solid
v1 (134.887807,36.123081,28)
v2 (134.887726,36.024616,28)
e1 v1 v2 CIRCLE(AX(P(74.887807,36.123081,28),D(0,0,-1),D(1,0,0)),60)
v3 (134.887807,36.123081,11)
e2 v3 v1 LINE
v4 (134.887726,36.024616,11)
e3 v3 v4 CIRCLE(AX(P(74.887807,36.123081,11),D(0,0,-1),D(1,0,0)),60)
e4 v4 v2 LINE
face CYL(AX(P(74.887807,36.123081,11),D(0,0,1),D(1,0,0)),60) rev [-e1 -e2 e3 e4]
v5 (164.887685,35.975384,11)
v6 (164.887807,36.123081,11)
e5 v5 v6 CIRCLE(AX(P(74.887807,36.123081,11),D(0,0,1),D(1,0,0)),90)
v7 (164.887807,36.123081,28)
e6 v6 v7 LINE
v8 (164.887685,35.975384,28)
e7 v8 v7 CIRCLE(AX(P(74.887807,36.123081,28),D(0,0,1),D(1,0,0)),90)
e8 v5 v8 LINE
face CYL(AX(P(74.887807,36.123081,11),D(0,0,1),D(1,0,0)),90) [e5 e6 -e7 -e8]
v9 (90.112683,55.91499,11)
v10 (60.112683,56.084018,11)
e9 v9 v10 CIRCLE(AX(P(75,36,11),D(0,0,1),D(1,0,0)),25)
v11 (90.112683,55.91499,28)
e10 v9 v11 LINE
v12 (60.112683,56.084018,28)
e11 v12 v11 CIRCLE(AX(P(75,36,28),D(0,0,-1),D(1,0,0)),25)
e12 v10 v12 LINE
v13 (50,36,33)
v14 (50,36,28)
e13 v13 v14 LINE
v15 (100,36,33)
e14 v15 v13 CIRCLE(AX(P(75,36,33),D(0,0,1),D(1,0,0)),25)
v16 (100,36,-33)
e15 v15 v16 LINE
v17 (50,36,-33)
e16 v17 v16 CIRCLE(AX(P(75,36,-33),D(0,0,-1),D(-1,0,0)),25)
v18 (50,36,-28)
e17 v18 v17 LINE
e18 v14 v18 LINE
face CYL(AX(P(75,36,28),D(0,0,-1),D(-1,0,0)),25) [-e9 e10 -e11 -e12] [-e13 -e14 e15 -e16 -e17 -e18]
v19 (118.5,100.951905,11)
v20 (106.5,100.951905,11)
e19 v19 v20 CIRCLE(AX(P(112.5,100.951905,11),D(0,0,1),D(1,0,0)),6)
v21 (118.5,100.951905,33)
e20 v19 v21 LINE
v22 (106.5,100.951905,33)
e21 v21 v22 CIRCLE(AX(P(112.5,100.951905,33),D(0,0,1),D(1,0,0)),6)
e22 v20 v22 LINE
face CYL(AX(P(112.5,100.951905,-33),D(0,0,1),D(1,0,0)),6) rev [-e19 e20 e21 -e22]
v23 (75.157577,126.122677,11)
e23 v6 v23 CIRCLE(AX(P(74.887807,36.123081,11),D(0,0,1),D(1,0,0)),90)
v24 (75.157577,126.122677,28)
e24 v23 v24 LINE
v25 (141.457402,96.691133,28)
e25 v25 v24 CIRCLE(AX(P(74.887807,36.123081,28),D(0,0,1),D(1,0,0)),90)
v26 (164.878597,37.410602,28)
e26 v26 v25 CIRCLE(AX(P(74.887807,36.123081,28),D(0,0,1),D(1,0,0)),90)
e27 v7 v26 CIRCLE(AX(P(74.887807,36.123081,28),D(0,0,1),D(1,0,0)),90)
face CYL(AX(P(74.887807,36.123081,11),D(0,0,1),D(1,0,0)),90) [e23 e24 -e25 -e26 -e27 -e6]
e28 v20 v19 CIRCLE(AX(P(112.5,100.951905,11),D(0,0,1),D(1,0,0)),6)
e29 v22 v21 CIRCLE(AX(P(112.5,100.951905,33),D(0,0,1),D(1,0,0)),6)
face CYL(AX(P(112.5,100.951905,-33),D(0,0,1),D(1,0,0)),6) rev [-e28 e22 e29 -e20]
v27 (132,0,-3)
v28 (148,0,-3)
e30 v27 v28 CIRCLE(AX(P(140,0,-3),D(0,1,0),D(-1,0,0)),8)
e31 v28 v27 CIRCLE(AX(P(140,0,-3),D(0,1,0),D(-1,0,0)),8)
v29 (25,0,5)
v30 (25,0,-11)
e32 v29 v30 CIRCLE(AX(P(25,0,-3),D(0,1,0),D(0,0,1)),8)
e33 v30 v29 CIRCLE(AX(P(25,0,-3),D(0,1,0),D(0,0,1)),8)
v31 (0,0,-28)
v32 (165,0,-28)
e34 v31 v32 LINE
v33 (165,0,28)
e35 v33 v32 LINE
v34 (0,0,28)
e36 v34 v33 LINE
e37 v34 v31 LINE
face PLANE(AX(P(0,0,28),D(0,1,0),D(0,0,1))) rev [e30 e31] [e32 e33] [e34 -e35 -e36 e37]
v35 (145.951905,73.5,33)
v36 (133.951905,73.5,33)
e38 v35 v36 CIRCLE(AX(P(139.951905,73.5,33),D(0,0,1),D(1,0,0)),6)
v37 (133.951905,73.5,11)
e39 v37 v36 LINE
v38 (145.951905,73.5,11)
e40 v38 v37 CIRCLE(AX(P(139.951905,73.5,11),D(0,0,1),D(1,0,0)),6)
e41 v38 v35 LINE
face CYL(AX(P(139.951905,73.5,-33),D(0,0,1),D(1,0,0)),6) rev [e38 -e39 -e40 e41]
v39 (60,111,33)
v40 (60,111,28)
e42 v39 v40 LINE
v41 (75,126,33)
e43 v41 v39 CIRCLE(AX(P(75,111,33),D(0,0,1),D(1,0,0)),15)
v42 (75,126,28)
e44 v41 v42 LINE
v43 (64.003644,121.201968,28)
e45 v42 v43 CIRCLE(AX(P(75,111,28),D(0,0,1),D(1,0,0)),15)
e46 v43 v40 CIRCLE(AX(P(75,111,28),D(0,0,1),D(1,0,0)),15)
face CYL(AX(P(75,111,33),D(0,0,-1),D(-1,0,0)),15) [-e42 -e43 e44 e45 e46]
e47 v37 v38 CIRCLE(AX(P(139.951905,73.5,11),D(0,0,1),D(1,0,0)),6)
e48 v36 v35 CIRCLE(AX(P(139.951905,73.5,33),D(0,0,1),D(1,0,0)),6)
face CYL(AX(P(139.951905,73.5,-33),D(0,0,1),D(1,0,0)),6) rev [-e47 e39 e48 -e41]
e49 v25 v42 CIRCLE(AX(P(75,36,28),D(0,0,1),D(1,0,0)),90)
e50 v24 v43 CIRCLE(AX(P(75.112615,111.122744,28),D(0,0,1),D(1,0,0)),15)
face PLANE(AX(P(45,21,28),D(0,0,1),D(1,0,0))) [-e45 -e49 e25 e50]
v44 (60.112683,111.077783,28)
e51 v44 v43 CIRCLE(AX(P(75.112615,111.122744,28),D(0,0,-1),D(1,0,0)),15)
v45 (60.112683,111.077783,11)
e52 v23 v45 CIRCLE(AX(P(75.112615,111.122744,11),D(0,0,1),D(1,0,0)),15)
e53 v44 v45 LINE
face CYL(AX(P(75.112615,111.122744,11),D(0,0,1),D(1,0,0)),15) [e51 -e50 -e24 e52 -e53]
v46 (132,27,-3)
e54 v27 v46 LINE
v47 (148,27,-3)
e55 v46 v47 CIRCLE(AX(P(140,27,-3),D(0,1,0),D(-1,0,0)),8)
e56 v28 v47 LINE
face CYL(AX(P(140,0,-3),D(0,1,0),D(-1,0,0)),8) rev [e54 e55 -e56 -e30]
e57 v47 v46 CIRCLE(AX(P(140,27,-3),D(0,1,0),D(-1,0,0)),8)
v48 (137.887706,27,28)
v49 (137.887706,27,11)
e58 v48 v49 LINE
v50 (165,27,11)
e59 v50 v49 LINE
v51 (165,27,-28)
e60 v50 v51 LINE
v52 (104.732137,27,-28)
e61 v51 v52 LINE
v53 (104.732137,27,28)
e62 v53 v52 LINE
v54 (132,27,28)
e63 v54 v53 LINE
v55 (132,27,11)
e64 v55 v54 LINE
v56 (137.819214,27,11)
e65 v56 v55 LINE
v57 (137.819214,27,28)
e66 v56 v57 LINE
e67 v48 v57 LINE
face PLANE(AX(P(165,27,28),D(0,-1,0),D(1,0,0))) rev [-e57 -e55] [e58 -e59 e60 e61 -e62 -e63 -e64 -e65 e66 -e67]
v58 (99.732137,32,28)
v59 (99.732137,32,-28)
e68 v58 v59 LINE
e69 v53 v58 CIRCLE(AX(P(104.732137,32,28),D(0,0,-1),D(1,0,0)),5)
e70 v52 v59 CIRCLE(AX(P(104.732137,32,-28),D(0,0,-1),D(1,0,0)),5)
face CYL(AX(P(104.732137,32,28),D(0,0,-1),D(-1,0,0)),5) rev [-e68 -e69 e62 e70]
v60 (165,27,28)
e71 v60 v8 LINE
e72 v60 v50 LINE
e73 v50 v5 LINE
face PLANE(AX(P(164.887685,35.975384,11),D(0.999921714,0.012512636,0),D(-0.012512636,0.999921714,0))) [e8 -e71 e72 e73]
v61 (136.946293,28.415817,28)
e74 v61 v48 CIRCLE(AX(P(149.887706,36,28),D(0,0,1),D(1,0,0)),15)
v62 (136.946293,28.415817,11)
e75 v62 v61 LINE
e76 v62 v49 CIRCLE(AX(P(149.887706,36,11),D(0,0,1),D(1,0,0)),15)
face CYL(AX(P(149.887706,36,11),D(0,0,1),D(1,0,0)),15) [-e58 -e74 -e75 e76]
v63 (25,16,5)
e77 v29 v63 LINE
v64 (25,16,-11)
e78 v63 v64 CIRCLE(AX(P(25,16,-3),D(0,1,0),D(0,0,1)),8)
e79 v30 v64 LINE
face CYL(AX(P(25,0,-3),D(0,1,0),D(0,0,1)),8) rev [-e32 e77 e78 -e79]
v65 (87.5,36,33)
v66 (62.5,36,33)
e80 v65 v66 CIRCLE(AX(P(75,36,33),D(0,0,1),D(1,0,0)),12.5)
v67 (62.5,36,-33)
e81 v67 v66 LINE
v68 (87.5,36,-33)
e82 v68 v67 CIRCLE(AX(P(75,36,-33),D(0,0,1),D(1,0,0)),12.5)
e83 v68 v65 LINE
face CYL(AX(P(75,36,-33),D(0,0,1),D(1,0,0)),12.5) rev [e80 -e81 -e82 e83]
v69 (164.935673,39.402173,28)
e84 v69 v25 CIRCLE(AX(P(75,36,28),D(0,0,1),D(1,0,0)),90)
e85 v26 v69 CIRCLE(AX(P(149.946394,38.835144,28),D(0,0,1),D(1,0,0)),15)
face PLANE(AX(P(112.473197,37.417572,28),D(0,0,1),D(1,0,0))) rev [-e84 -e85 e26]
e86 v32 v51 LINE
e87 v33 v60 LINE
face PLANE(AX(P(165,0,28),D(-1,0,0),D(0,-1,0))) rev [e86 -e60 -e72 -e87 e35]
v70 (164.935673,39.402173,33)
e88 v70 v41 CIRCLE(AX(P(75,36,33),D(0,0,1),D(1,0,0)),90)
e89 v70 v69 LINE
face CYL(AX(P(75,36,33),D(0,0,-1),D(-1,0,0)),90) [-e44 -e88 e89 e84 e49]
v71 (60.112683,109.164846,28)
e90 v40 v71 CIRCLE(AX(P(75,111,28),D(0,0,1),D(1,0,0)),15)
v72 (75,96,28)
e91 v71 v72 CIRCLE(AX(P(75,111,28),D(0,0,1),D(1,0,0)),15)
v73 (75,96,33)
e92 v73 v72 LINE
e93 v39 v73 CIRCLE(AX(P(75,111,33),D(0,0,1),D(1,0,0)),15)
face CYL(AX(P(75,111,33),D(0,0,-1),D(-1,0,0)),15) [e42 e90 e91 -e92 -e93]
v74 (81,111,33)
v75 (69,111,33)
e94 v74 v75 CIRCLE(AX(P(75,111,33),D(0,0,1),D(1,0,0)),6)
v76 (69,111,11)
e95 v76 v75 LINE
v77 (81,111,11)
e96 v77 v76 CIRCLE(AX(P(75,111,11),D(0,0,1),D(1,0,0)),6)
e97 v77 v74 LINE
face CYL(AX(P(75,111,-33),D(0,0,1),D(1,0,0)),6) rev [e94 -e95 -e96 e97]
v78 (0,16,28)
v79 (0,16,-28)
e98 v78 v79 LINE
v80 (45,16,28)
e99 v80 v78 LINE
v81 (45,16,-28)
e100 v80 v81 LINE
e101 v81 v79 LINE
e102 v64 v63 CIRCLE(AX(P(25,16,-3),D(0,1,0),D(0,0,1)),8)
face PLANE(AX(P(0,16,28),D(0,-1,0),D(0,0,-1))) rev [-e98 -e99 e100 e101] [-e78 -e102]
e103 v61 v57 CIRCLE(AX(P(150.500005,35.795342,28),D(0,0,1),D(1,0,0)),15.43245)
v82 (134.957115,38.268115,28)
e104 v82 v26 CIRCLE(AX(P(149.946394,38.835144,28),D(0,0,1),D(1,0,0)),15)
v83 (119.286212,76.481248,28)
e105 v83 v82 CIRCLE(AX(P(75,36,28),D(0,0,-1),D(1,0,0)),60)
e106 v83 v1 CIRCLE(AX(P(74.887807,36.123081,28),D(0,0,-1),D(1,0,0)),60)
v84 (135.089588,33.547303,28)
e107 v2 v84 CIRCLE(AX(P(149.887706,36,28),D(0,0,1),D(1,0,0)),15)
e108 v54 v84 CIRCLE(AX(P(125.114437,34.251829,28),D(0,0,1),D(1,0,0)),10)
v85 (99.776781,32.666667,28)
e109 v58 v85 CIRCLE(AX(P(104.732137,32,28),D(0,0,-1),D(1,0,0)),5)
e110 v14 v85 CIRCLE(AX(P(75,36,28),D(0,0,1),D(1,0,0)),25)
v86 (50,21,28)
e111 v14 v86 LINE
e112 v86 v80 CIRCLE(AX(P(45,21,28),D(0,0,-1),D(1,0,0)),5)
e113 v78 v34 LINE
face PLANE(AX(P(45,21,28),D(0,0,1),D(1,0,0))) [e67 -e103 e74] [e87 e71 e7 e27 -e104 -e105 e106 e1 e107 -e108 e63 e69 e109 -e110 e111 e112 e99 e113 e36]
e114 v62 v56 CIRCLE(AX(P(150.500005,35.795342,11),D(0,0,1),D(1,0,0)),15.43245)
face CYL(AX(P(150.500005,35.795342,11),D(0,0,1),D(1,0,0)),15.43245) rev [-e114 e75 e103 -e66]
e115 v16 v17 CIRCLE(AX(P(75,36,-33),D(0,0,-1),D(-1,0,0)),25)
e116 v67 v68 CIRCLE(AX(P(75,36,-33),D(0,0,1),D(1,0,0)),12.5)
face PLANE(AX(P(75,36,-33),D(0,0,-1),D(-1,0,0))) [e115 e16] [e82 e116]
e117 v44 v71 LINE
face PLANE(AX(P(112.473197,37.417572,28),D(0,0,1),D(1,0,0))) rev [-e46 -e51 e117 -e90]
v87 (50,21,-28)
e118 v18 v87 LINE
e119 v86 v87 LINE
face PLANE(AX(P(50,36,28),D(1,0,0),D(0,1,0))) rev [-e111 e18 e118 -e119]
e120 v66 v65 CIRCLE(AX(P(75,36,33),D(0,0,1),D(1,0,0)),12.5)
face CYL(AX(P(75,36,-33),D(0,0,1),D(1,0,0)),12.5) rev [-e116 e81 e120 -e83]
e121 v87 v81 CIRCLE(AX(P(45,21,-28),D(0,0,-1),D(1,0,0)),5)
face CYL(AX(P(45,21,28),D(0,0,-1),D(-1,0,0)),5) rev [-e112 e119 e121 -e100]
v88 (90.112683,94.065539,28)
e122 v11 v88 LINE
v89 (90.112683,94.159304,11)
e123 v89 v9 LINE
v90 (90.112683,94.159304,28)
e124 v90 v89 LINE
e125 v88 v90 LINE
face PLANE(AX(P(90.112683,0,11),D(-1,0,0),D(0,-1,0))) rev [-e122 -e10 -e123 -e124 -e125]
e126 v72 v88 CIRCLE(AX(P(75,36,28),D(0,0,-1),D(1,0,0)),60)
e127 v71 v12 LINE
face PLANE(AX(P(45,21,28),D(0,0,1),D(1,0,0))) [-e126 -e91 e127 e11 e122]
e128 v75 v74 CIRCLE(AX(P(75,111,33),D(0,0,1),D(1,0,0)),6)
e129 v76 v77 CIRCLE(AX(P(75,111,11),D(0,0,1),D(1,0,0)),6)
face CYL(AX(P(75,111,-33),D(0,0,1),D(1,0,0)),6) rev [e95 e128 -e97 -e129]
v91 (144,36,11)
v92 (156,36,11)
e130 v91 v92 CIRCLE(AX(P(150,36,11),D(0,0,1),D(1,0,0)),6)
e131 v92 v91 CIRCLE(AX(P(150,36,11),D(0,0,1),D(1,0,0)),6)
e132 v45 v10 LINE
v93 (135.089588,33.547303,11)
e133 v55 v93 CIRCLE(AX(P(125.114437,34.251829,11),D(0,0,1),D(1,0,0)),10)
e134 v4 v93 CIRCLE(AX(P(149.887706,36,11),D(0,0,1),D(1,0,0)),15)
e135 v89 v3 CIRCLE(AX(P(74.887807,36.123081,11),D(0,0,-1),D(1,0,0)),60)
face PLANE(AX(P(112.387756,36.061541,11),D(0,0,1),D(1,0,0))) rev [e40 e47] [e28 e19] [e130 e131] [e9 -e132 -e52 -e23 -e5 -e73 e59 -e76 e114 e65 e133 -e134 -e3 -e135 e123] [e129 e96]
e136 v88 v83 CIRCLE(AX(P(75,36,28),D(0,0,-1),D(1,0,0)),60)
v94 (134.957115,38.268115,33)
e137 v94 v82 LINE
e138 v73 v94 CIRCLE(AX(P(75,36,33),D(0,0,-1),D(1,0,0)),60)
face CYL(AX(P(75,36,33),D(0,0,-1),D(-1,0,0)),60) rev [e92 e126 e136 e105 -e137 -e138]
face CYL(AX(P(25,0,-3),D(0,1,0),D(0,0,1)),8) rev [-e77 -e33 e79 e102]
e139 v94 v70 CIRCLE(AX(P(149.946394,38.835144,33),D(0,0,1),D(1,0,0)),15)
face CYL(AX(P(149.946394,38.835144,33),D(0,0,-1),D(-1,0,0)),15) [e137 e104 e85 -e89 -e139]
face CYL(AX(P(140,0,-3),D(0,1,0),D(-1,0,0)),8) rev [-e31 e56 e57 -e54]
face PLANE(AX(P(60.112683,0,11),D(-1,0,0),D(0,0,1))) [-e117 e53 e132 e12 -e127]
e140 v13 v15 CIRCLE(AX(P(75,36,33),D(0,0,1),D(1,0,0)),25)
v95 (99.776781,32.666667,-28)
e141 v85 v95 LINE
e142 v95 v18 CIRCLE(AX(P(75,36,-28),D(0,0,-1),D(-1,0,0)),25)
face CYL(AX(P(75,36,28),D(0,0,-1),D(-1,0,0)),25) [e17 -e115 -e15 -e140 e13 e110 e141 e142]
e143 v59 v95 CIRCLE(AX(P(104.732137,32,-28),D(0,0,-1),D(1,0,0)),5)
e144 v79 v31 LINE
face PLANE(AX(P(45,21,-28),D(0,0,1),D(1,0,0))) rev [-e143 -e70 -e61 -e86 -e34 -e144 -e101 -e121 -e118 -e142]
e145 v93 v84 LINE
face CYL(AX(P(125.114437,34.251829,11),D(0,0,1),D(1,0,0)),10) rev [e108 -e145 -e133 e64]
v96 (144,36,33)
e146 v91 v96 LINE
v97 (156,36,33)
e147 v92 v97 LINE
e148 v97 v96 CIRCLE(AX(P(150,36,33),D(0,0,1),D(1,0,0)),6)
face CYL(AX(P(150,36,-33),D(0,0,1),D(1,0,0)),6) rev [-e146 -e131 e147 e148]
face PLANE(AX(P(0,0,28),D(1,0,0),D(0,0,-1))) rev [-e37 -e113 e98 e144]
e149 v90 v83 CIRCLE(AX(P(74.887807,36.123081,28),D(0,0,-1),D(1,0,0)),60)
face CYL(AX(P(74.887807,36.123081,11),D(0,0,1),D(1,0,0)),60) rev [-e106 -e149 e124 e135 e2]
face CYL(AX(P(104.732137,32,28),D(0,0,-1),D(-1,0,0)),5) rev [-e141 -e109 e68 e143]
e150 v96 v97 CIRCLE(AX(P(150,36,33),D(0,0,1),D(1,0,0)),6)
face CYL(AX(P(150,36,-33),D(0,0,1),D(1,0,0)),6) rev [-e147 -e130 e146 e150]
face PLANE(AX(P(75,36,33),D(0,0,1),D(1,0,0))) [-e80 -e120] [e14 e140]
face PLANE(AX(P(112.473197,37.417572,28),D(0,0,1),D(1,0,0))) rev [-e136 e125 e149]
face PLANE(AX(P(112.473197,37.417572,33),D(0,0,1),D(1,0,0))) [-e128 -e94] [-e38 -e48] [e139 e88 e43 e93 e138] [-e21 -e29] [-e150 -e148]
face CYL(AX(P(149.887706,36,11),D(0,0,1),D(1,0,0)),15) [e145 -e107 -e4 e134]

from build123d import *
from build123d.topology import SkipClean

# Parameters (mm, degrees)
BASE_AND_HUB_BODY_DEPTH       = 28
FRONT_START                   = 5
FRONT_HUB_BOSS_SKETCH_R       = 25
FRONT_HUB_BOSS_50_DEPTH       = 5
REAR_HUB_BOSS_SKETCH_R        = 25
REAR_HUB_BOSS_50_DEPTH        = 5
BEARING_BORE_SKETCH_R         = 12.5
BEARING_BORE_25_DEPTH         = 188.888264668
HUB_SLOT_SKETCH_R             = 8
HUB_SLOT_CUT_DEPTH            = 175.180940404
BASE_SLOT_SKETCH_R            = 8
BASE_SLOT_CUT_DEPTH           = 172.668284782
FLANGE_ARM_DEPTH              = 17
ARM_WEB_DEPTH                 = 22
WEB_RELIEF_CUT_DEPTH          = 5
FLANGE_RIM_DEPTH              = 5
ARM_FOOT_FILL_DEPTH           = 17
ARM_INFILL_DEPTH              = 17
FLANGE_BOLT_HOLES_SKETCH_R    = 6
FLANGE_BOLT_HOLES_4X_12_DEPTH = 218.917293143


with BuildPart() as part:
    # Base and Hub Profile Sketch → Base and Hub Body (new, symmetric)
    with BuildSketch(Plane.XY):
        with BuildLine():
            Line((0, 0), (165, 0))
            Line((165, 0), (165, 27))
            Line((165, 27), (104.732137495, 27))
            ThreePointArc((104.732137495, 27), (100.968274231, 28.708597057), (99.776781246, 32.666666667))
            ThreePointArc((99.776781246, 32.666666667), (76.670399482, 60.944132889), (50, 36))
            Line((50, 36), (50, 21))
            ThreePointArc((50, 21), (48.535533906, 17.464466094), (45, 16))
            Line((45, 16), (0, 16))
            Line((0, 16), (0, 0))
        make_face()
    extrude(amount=BASE_AND_HUB_BODY_DEPTH, both=True)

    # Front Hub Boss Sketch → Front Hub Boss Ø50 (add)
    with BuildSketch(Plane.XY.offset(28).offset(FRONT_START)):
        with Locations(Location((75, 36, 0), (0, 0, 180))):
            Circle(FRONT_HUB_BOSS_SKETCH_R)
    extrude(amount=-FRONT_HUB_BOSS_50_DEPTH)

    # Rear Hub Boss Sketch → Rear Hub Boss Ø50 (add)
    with SkipClean():  # the faces are left unmerged after this step: merging them gives an invalid solid
        with BuildSketch(Plane(origin=(0, 0, -28), x_dir=(-1, 0, 0), z_dir=(0, 0, -1))):
            with Locations((-75, 36)):
                Circle(REAR_HUB_BOSS_SKETCH_R)
        extrude(amount=REAR_HUB_BOSS_50_DEPTH)

    # Bearing Bore Sketch → Bearing Bore Ø25 (cut, through all)
    with SkipClean():  # the faces are left unmerged after this step: merging them gives an invalid solid
        with BuildSketch(Plane.XY.offset(33)):
            with Locations((75, 36)):
                Circle(BEARING_BORE_SKETCH_R)
        extrude(amount=-BEARING_BORE_25_DEPTH, mode=Mode.SUBTRACT)

    # Hub Slot Sketch → Hub Slot Cut (cut, through all)
    with SkipClean():  # the faces are left unmerged after this step: merging them gives an invalid solid
        with BuildSketch(Plane(origin=(0, 16, 0), x_dir=(1, 0, 0), z_dir=(0, 1, 0))):
            with Locations(Location((25, 3, 0), (0, 0, 270))):
                Circle(HUB_SLOT_SKETCH_R)
        extrude(amount=-HUB_SLOT_CUT_DEPTH, mode=Mode.SUBTRACT)

    # Base Slot Sketch → Base Slot Cut (cut, through all)
    with SkipClean():  # the faces are left unmerged after this step: merging them gives an invalid solid
        with BuildSketch(Plane(origin=(0, 27, 0), x_dir=(1, 0, 0), z_dir=(0, 1, 0))):
            with Locations(Location((140, 3, 0), (0, 0, 180))):
                Circle(BASE_SLOT_SKETCH_R)
        extrude(amount=-BASE_SLOT_CUT_DEPTH, mode=Mode.SUBTRACT)

    # Flange Arm Sketch → Flange Arm (add)
    with SkipClean():  # the faces are left unmerged after this step: merging them gives an invalid solid
        with BuildSketch(Plane.XY.offset(28)):
            with BuildLine():
                ThreePointArc((164.887685495, 35.975383738), (138.674843146, 99.614923148), (75.157577255, 126.122676998))
                ThreePointArc((75.157577255, 126.122676998), (60.112682879, 111.167706145), (75.067653733, 96.122811769))
                ThreePointArc((75.067653733, 96.122811769), (117.41249766, 78.450975869), (134.887725893, 36.024616262))
                ThreePointArc((134.887725893, 36.024616262), (149.863089432, 21.000020199), (164.887685495, 35.975383738))
            make_face()
        extrude(amount=-FLANGE_ARM_DEPTH)

    # Arm Web Sketch → Arm Web (add)
    with SkipClean():  # the faces are left unmerged after this step: merging them gives an invalid solid
        with BuildSketch(Plane.XY.offset(33)):
            with BuildLine():
                Line((90.112682879, 111.167706145), (60.112682879, 111.167706145))
                Line((60.112682879, 111.167706145), (60.112682879, 56.084018247))
                ThreePointArc((60.112682879, 56.084018247), (75.140854857, 60.999603195), (90.112682879, 55.914989736))
                Line((90.112682879, 55.914989736), (90.112682879, 111.167706145))
            make_face()
        extrude(amount=-ARM_WEB_DEPTH)

    # Web Relief Sketch → Web Relief Cut (cut)
    with SkipClean():  # the faces are left unmerged after this step: merging them gives an invalid solid
        with BuildSketch(Plane.XY.offset(33)):
            with BuildLine():
                Line((60.112682879, 56.084018247), (60.112682879, 112.084018247))
                Line((60.112682879, 112.084018247), (90.112682879, 112.084018247))
                Line((90.112682879, 112.084018247), (90.112682879, 55.914989736))
                ThreePointArc((90.112682879, 55.914989736), (75.140854857, 60.999603195), (60.112682879, 56.084018247))
            make_face()
        extrude(amount=-WEB_RELIEF_CUT_DEPTH, mode=Mode.SUBTRACT)

    # Flange Rim Sketch → Flange Rim (add)
    with SkipClean():  # the faces are left unmerged after this step: merging them gives an invalid solid
        with BuildSketch(Plane.XY.offset(28)):
            with BuildLine():
                ThreePointArc((164.935672679, 39.402172812), (137.425172995, 100.831302444), (75, 126))
                ThreePointArc((75, 126), (60, 111), (75, 96))
                ThreePointArc((75, 96), (116.616781997, 79.220868296), (134.957115119, 38.268115208))
                ThreePointArc((134.957115119, 38.268115208), (150.513422701, 23.84586523), (164.935672679, 39.402172812))
            make_face()
        extrude(amount=FLANGE_RIM_DEPTH)

    # Arm Foot Fill Sketch → Arm Foot Fill (add)
    with SkipClean():  # the faces are left unmerged after this step: merging them gives an invalid solid
        with BuildSketch(Plane.XY.offset(28)):
            with BuildLine():
                ThreePointArc((135.089588319, 33.547303087), (134.158093135, 29.984243626), (132, 27))
                Line((132, 27), (137.819213879, 27))
                ThreePointArc((137.819213879, 27), (137.363665204, 27.696139518), (136.94629296, 28.415816692))
                ThreePointArc((136.94629296, 28.415816692), (135.782620766, 30.896415066), (135.089588319, 33.547303087))
            make_face()
        extrude(amount=-ARM_FOOT_FILL_DEPTH)

    # Arm Infill Sketch → Arm Infill (add)
    with SkipClean():  # the faces are left unmerged after this step: merging them gives an invalid solid
        with BuildSketch(Plane.XY.offset(28)):
            with BuildLine():
                Line((161.887705694, 27), (165, 27))
                Line((165, 27), (164.887685495, 35.975383738))
                ThreePointArc((164.887685495, 35.975383738), (164.1140582, 31.244908584), (161.887705694, 27))
            make_face()
        extrude(amount=-ARM_INFILL_DEPTH)

    # Flange Bolt Holes Sketch → Flange Bolt Holes 4xØ12 (cut, through all)
    with SkipClean():  # the faces are left unmerged after this step: merging them gives an invalid solid
        with BuildSketch(Plane.XY.offset(33)):
            with Locations((150, 36)):
                Circle(FLANGE_BOLT_HOLES_SKETCH_R)
            with Locations((75, 111)):
                Circle(FLANGE_BOLT_HOLES_SKETCH_R)
            with Locations((112.5, 100.951905284)):
                Circle(FLANGE_BOLT_HOLES_SKETCH_R)
            with Locations((139.951905284, 73.5)):
                Circle(FLANGE_BOLT_HOLES_SKETCH_R)
        extrude(amount=-FLANGE_BOLT_HOLES_4X_12_DEPTH, mode=Mode.SUBTRACT)


solid = part.part
